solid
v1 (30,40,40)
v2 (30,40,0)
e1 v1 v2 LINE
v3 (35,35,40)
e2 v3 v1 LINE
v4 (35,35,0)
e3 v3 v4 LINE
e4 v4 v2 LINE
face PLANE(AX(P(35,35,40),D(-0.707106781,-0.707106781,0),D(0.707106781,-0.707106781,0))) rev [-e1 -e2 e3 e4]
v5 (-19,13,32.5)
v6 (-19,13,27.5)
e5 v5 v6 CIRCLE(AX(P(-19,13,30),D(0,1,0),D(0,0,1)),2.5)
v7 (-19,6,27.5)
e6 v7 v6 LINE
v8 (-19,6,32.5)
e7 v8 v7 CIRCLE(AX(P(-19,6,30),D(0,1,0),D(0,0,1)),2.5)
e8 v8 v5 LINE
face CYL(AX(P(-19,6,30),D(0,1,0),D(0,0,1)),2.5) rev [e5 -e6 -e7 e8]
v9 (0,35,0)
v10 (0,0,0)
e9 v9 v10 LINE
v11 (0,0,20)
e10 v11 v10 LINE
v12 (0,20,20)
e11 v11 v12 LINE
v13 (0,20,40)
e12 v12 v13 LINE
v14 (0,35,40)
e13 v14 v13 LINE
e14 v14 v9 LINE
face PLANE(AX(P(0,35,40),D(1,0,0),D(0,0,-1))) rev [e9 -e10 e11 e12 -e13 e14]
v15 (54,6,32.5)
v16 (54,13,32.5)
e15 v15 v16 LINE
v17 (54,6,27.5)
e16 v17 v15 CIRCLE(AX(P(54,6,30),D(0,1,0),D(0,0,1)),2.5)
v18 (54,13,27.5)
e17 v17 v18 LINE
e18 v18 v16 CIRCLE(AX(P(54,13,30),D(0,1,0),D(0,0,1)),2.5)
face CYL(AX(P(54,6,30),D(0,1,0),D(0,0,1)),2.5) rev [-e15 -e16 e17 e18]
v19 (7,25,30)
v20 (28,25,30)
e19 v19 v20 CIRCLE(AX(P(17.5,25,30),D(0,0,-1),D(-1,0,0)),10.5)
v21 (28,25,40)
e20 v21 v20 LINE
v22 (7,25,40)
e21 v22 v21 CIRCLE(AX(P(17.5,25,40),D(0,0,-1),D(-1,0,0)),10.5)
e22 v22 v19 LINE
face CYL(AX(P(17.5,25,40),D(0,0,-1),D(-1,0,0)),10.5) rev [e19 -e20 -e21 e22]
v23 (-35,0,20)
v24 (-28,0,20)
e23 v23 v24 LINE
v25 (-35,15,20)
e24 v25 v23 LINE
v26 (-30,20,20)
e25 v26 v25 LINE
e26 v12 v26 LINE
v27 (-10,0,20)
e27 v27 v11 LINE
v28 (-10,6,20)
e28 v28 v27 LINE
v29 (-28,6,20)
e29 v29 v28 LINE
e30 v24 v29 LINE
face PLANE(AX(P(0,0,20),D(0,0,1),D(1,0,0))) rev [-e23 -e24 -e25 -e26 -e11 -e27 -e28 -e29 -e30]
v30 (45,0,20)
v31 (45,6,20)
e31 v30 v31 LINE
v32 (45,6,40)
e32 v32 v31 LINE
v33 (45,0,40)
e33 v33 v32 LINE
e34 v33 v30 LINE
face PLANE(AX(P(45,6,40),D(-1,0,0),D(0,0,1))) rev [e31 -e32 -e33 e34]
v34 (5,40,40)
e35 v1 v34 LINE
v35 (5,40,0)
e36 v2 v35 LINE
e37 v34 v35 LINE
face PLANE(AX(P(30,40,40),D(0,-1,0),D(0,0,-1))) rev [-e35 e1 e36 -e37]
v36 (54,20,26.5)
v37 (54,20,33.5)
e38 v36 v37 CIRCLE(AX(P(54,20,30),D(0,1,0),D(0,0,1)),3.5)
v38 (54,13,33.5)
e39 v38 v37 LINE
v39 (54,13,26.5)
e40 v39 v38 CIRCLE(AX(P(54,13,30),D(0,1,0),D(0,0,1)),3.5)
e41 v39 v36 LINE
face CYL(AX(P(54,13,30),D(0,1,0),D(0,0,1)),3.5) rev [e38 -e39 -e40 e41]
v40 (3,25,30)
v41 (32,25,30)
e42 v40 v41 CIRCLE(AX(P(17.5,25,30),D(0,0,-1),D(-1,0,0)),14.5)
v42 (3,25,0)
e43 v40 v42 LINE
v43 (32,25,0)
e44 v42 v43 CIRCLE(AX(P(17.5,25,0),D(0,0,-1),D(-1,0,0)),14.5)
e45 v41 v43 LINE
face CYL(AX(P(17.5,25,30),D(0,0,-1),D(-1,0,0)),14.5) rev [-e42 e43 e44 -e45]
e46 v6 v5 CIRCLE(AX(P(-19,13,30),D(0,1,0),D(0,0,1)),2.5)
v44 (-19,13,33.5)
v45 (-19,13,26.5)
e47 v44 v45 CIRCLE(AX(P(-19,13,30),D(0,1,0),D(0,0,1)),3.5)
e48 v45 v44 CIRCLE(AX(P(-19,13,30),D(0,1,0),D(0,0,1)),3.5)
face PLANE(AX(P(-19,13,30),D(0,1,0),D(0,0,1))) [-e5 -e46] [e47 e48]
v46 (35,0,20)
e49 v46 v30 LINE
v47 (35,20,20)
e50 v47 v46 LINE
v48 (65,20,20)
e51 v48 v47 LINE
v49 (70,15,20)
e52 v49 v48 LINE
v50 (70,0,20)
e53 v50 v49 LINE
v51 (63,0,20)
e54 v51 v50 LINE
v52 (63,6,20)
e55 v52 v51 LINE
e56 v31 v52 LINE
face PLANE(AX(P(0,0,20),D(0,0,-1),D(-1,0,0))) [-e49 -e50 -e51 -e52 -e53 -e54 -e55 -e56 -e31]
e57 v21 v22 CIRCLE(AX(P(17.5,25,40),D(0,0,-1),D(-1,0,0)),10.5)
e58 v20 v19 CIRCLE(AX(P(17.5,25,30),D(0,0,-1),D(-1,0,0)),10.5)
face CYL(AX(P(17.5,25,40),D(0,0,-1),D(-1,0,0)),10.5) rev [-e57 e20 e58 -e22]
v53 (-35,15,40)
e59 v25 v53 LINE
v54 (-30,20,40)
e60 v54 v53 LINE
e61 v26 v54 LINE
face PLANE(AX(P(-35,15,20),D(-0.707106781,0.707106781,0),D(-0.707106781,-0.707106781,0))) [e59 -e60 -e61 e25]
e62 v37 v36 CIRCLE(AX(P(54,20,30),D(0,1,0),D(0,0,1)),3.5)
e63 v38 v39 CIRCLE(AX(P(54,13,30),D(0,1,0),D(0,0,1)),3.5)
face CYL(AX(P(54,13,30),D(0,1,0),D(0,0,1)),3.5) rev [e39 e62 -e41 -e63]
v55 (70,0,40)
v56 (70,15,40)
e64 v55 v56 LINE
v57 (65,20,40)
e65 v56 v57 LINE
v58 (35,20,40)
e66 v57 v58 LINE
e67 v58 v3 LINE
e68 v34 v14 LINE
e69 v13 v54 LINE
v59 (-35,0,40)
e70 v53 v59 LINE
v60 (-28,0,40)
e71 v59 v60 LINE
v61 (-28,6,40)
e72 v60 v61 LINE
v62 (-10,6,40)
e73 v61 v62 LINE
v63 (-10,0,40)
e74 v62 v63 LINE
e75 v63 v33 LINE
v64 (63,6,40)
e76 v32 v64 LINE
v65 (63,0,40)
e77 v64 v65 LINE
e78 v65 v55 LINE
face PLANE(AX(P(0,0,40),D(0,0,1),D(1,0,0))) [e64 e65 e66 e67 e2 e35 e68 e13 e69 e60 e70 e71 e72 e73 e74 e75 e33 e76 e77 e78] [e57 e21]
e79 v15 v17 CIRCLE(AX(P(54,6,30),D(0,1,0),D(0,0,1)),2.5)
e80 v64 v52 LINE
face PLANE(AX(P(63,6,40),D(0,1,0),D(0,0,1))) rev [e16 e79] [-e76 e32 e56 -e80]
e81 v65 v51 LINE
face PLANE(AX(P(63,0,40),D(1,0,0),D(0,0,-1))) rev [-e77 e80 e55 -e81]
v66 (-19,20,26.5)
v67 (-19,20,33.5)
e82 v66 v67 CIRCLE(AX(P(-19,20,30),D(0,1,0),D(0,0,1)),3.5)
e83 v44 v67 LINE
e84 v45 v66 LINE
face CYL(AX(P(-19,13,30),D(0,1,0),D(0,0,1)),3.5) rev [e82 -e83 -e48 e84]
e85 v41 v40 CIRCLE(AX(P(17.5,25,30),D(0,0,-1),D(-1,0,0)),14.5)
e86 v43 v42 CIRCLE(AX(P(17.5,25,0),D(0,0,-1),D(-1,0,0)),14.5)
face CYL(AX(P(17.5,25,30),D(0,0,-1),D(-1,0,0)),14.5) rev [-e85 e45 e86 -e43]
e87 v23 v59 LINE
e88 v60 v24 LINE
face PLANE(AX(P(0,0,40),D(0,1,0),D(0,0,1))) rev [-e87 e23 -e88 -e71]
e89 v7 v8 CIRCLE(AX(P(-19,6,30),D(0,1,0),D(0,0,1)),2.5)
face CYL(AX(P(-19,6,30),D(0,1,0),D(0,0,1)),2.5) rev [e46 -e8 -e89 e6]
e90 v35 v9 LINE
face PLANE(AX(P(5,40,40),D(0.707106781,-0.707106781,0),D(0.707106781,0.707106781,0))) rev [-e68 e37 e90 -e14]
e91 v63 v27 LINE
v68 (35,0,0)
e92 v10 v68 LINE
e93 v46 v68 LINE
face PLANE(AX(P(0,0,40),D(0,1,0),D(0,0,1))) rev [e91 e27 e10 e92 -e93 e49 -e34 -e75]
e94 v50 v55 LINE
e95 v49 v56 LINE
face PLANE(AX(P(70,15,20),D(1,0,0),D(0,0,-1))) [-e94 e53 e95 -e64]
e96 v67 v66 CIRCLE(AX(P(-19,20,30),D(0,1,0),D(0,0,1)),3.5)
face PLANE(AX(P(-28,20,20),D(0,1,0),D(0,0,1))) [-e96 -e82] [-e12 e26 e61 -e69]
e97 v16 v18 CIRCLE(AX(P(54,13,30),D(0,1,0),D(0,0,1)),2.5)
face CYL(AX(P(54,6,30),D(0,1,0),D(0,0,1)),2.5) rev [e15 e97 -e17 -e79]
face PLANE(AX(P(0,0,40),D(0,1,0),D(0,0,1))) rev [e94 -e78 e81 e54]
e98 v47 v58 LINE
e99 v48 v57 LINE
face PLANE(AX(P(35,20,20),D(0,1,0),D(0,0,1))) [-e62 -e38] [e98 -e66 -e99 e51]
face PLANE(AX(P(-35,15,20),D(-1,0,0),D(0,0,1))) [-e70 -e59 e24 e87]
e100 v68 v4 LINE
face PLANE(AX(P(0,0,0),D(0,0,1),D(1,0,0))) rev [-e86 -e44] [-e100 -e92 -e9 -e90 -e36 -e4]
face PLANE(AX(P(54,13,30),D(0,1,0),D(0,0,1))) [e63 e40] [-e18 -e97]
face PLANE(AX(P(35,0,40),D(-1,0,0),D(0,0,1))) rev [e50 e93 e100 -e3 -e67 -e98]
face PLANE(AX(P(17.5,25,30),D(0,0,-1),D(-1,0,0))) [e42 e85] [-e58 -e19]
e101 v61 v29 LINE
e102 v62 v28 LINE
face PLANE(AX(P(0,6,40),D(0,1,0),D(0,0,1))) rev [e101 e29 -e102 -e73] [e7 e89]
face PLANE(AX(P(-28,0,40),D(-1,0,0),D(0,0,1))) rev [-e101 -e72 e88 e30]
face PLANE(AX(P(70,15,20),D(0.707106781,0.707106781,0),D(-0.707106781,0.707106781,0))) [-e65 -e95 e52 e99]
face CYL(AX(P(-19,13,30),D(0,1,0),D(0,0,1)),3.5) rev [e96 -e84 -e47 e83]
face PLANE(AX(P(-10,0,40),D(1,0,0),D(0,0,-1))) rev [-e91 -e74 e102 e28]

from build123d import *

# Parameters (mm, degrees)
BASE_BODY_DEPTH             = 40
MOUNTING_LUG_1_DEPTH        = 20
MOUNTING_LUG_2_DEPTH        = 20
LUG_2_BOTTOM_SLOT_PROFILE_W = 18
LUG_2_BOTTOM_SLOT_PROFILE_H = 6
LUG_2_BOTTOM_SLOT_DEPTH     = 20
LUG_1_BOTTOM_SLOT_PROFILE_W = 18
LUG_1_BOTTOM_SLOT_PROFILE_H = 6
LUG_1_BOTTOM_SLOT_DEPTH     = 20
LUG_2_HOLE_7_SKETCH_R       = 3.5
LUG_2_HOLE_7_DEPTH          = 7
LUG_2_HOLE_5_SKETCH_R       = 2.5
LUG_2_HOLE_5_DEPTH          = 7
LUG_1_HOLE_7_SKETCH_R       = 3.5
LUG_1_HOLE_7_DEPTH          = 7
LUG_1_HOLE_5_SKETCH_R       = 2.5
LUG_1_HOLE_5_DEPTH          = 7
BEARING_BORE_29_SKETCH_R    = 14.5
BEARING_BORE_29_DEPTH       = 30
THROUGH_BORE_21_SKETCH_R    = 10.5
THROUGH_BORE_21_DEPTH       = 87.02325267


with BuildPart() as part:
    # Base Body Profile → Base Body (new body)
    with BuildSketch(Plane.XY):
        Polygon((0, 0), (35, 0), (35, 35), (30, 40), (5, 40), (0, 35), align=None)
    extrude(amount=BASE_BODY_DEPTH)

    # Mounting Lug 1 Profile → Mounting Lug 1 (add)
    with BuildSketch(Plane.XY.offset(40)):
        Polygon((0, 0), (0, 20), (-19, 20), (-28, 20), (-30, 20), (-35, 15), (-35, 0), align=None)
    extrude(amount=-MOUNTING_LUG_1_DEPTH)

    # Mounting Lug 2 Profile → Mounting Lug 2 (add)
    with BuildSketch(Plane.XY.offset(40)):
        Polygon((35, 0), (35, 20), (54, 20), (63, 20), (65, 20), (70, 15), (70, 0), align=None)
    extrude(amount=-MOUNTING_LUG_2_DEPTH)

    # Lug 2 Bottom Slot Profile → Lug 2 Bottom Slot (cut)
    with BuildSketch(Plane(origin=(0, 0, 20), x_dir=(-1, 0, 0), z_dir=(0, 0, -1))):
        with Locations((-54, 3)):
            Rectangle(LUG_2_BOTTOM_SLOT_PROFILE_W, LUG_2_BOTTOM_SLOT_PROFILE_H)
    extrude(amount=-LUG_2_BOTTOM_SLOT_DEPTH, mode=Mode.SUBTRACT)

    # Lug 1 Bottom Slot Profile → Lug 1 Bottom Slot (cut)
    with BuildSketch(Plane(origin=(0, 0, 20), x_dir=(-1, 0, 0), z_dir=(0, 0, -1))):
        with Locations((19, 3)):
            Rectangle(LUG_1_BOTTOM_SLOT_PROFILE_W, LUG_1_BOTTOM_SLOT_PROFILE_H)
    extrude(amount=-LUG_1_BOTTOM_SLOT_DEPTH, mode=Mode.SUBTRACT)

    # Lug 2 Hole Ø7 Sketch → Lug 2 Hole Ø7 (cut)
    with BuildSketch(Plane(origin=(0, 20, 0), x_dir=(1, 0, 0), z_dir=(0, 1, 0))):
        with Locations(Location((54, -30, 0), (0, 0, 270))):
            Circle(LUG_2_HOLE_7_SKETCH_R)
    extrude(amount=-LUG_2_HOLE_7_DEPTH, mode=Mode.SUBTRACT)

    # Lug 2 Hole Ø5 Sketch → Lug 2 Hole Ø5 (cut)
    with BuildSketch(Plane(origin=(0, 13, 0), x_dir=(1, 0, 0), z_dir=(0, 1, 0))):
        with Locations(Location((54, -30, 0), (0, 0, 270))):
            Circle(LUG_2_HOLE_5_SKETCH_R)
    extrude(amount=-LUG_2_HOLE_5_DEPTH, mode=Mode.SUBTRACT)

    # Lug 1 Hole Ø7 Sketch → Lug 1 Hole Ø7 (cut)
    with BuildSketch(Plane(origin=(0, 20, 0), x_dir=(1, 0, 0), z_dir=(0, 1, 0))):
        with Locations(Location((-19, -30, 0), (0, 0, 270))):
            Circle(LUG_1_HOLE_7_SKETCH_R)
    extrude(amount=-LUG_1_HOLE_7_DEPTH, mode=Mode.SUBTRACT)

    # Lug 1 Hole Ø5 Sketch → Lug 1 Hole Ø5 (cut)
    with BuildSketch(Plane(origin=(0, 13, 0), x_dir=(1, 0, 0), z_dir=(0, 1, 0))):
        with Locations(Location((-19, -30, 0), (0, 0, 270))):
            Circle(LUG_1_HOLE_5_SKETCH_R)
    extrude(amount=-LUG_1_HOLE_5_DEPTH, mode=Mode.SUBTRACT)

    # Bearing Bore Ø29 Sketch → Bearing Bore Ø29 (cut)
    with BuildSketch(Plane(origin=(0, 0, 0), x_dir=(-1, 0, 0), z_dir=(0, 0, -1))):
        with Locations((-17.5, 25)):
            Circle(BEARING_BORE_29_SKETCH_R)
    extrude(amount=-BEARING_BORE_29_DEPTH, mode=Mode.SUBTRACT)

    # Through Bore Ø21 Sketch → Through Bore Ø21 (cut, through all)
    with BuildSketch(Plane(origin=(0, 0, 30), x_dir=(-1, 0, 0), z_dir=(0, 0, -1))):
        with Locations((-17.5, 25)):
            Circle(THROUGH_BORE_21_SKETCH_R)
    extrude(amount=-THROUGH_BORE_21_DEPTH, mode=Mode.SUBTRACT)


solid = part.part
